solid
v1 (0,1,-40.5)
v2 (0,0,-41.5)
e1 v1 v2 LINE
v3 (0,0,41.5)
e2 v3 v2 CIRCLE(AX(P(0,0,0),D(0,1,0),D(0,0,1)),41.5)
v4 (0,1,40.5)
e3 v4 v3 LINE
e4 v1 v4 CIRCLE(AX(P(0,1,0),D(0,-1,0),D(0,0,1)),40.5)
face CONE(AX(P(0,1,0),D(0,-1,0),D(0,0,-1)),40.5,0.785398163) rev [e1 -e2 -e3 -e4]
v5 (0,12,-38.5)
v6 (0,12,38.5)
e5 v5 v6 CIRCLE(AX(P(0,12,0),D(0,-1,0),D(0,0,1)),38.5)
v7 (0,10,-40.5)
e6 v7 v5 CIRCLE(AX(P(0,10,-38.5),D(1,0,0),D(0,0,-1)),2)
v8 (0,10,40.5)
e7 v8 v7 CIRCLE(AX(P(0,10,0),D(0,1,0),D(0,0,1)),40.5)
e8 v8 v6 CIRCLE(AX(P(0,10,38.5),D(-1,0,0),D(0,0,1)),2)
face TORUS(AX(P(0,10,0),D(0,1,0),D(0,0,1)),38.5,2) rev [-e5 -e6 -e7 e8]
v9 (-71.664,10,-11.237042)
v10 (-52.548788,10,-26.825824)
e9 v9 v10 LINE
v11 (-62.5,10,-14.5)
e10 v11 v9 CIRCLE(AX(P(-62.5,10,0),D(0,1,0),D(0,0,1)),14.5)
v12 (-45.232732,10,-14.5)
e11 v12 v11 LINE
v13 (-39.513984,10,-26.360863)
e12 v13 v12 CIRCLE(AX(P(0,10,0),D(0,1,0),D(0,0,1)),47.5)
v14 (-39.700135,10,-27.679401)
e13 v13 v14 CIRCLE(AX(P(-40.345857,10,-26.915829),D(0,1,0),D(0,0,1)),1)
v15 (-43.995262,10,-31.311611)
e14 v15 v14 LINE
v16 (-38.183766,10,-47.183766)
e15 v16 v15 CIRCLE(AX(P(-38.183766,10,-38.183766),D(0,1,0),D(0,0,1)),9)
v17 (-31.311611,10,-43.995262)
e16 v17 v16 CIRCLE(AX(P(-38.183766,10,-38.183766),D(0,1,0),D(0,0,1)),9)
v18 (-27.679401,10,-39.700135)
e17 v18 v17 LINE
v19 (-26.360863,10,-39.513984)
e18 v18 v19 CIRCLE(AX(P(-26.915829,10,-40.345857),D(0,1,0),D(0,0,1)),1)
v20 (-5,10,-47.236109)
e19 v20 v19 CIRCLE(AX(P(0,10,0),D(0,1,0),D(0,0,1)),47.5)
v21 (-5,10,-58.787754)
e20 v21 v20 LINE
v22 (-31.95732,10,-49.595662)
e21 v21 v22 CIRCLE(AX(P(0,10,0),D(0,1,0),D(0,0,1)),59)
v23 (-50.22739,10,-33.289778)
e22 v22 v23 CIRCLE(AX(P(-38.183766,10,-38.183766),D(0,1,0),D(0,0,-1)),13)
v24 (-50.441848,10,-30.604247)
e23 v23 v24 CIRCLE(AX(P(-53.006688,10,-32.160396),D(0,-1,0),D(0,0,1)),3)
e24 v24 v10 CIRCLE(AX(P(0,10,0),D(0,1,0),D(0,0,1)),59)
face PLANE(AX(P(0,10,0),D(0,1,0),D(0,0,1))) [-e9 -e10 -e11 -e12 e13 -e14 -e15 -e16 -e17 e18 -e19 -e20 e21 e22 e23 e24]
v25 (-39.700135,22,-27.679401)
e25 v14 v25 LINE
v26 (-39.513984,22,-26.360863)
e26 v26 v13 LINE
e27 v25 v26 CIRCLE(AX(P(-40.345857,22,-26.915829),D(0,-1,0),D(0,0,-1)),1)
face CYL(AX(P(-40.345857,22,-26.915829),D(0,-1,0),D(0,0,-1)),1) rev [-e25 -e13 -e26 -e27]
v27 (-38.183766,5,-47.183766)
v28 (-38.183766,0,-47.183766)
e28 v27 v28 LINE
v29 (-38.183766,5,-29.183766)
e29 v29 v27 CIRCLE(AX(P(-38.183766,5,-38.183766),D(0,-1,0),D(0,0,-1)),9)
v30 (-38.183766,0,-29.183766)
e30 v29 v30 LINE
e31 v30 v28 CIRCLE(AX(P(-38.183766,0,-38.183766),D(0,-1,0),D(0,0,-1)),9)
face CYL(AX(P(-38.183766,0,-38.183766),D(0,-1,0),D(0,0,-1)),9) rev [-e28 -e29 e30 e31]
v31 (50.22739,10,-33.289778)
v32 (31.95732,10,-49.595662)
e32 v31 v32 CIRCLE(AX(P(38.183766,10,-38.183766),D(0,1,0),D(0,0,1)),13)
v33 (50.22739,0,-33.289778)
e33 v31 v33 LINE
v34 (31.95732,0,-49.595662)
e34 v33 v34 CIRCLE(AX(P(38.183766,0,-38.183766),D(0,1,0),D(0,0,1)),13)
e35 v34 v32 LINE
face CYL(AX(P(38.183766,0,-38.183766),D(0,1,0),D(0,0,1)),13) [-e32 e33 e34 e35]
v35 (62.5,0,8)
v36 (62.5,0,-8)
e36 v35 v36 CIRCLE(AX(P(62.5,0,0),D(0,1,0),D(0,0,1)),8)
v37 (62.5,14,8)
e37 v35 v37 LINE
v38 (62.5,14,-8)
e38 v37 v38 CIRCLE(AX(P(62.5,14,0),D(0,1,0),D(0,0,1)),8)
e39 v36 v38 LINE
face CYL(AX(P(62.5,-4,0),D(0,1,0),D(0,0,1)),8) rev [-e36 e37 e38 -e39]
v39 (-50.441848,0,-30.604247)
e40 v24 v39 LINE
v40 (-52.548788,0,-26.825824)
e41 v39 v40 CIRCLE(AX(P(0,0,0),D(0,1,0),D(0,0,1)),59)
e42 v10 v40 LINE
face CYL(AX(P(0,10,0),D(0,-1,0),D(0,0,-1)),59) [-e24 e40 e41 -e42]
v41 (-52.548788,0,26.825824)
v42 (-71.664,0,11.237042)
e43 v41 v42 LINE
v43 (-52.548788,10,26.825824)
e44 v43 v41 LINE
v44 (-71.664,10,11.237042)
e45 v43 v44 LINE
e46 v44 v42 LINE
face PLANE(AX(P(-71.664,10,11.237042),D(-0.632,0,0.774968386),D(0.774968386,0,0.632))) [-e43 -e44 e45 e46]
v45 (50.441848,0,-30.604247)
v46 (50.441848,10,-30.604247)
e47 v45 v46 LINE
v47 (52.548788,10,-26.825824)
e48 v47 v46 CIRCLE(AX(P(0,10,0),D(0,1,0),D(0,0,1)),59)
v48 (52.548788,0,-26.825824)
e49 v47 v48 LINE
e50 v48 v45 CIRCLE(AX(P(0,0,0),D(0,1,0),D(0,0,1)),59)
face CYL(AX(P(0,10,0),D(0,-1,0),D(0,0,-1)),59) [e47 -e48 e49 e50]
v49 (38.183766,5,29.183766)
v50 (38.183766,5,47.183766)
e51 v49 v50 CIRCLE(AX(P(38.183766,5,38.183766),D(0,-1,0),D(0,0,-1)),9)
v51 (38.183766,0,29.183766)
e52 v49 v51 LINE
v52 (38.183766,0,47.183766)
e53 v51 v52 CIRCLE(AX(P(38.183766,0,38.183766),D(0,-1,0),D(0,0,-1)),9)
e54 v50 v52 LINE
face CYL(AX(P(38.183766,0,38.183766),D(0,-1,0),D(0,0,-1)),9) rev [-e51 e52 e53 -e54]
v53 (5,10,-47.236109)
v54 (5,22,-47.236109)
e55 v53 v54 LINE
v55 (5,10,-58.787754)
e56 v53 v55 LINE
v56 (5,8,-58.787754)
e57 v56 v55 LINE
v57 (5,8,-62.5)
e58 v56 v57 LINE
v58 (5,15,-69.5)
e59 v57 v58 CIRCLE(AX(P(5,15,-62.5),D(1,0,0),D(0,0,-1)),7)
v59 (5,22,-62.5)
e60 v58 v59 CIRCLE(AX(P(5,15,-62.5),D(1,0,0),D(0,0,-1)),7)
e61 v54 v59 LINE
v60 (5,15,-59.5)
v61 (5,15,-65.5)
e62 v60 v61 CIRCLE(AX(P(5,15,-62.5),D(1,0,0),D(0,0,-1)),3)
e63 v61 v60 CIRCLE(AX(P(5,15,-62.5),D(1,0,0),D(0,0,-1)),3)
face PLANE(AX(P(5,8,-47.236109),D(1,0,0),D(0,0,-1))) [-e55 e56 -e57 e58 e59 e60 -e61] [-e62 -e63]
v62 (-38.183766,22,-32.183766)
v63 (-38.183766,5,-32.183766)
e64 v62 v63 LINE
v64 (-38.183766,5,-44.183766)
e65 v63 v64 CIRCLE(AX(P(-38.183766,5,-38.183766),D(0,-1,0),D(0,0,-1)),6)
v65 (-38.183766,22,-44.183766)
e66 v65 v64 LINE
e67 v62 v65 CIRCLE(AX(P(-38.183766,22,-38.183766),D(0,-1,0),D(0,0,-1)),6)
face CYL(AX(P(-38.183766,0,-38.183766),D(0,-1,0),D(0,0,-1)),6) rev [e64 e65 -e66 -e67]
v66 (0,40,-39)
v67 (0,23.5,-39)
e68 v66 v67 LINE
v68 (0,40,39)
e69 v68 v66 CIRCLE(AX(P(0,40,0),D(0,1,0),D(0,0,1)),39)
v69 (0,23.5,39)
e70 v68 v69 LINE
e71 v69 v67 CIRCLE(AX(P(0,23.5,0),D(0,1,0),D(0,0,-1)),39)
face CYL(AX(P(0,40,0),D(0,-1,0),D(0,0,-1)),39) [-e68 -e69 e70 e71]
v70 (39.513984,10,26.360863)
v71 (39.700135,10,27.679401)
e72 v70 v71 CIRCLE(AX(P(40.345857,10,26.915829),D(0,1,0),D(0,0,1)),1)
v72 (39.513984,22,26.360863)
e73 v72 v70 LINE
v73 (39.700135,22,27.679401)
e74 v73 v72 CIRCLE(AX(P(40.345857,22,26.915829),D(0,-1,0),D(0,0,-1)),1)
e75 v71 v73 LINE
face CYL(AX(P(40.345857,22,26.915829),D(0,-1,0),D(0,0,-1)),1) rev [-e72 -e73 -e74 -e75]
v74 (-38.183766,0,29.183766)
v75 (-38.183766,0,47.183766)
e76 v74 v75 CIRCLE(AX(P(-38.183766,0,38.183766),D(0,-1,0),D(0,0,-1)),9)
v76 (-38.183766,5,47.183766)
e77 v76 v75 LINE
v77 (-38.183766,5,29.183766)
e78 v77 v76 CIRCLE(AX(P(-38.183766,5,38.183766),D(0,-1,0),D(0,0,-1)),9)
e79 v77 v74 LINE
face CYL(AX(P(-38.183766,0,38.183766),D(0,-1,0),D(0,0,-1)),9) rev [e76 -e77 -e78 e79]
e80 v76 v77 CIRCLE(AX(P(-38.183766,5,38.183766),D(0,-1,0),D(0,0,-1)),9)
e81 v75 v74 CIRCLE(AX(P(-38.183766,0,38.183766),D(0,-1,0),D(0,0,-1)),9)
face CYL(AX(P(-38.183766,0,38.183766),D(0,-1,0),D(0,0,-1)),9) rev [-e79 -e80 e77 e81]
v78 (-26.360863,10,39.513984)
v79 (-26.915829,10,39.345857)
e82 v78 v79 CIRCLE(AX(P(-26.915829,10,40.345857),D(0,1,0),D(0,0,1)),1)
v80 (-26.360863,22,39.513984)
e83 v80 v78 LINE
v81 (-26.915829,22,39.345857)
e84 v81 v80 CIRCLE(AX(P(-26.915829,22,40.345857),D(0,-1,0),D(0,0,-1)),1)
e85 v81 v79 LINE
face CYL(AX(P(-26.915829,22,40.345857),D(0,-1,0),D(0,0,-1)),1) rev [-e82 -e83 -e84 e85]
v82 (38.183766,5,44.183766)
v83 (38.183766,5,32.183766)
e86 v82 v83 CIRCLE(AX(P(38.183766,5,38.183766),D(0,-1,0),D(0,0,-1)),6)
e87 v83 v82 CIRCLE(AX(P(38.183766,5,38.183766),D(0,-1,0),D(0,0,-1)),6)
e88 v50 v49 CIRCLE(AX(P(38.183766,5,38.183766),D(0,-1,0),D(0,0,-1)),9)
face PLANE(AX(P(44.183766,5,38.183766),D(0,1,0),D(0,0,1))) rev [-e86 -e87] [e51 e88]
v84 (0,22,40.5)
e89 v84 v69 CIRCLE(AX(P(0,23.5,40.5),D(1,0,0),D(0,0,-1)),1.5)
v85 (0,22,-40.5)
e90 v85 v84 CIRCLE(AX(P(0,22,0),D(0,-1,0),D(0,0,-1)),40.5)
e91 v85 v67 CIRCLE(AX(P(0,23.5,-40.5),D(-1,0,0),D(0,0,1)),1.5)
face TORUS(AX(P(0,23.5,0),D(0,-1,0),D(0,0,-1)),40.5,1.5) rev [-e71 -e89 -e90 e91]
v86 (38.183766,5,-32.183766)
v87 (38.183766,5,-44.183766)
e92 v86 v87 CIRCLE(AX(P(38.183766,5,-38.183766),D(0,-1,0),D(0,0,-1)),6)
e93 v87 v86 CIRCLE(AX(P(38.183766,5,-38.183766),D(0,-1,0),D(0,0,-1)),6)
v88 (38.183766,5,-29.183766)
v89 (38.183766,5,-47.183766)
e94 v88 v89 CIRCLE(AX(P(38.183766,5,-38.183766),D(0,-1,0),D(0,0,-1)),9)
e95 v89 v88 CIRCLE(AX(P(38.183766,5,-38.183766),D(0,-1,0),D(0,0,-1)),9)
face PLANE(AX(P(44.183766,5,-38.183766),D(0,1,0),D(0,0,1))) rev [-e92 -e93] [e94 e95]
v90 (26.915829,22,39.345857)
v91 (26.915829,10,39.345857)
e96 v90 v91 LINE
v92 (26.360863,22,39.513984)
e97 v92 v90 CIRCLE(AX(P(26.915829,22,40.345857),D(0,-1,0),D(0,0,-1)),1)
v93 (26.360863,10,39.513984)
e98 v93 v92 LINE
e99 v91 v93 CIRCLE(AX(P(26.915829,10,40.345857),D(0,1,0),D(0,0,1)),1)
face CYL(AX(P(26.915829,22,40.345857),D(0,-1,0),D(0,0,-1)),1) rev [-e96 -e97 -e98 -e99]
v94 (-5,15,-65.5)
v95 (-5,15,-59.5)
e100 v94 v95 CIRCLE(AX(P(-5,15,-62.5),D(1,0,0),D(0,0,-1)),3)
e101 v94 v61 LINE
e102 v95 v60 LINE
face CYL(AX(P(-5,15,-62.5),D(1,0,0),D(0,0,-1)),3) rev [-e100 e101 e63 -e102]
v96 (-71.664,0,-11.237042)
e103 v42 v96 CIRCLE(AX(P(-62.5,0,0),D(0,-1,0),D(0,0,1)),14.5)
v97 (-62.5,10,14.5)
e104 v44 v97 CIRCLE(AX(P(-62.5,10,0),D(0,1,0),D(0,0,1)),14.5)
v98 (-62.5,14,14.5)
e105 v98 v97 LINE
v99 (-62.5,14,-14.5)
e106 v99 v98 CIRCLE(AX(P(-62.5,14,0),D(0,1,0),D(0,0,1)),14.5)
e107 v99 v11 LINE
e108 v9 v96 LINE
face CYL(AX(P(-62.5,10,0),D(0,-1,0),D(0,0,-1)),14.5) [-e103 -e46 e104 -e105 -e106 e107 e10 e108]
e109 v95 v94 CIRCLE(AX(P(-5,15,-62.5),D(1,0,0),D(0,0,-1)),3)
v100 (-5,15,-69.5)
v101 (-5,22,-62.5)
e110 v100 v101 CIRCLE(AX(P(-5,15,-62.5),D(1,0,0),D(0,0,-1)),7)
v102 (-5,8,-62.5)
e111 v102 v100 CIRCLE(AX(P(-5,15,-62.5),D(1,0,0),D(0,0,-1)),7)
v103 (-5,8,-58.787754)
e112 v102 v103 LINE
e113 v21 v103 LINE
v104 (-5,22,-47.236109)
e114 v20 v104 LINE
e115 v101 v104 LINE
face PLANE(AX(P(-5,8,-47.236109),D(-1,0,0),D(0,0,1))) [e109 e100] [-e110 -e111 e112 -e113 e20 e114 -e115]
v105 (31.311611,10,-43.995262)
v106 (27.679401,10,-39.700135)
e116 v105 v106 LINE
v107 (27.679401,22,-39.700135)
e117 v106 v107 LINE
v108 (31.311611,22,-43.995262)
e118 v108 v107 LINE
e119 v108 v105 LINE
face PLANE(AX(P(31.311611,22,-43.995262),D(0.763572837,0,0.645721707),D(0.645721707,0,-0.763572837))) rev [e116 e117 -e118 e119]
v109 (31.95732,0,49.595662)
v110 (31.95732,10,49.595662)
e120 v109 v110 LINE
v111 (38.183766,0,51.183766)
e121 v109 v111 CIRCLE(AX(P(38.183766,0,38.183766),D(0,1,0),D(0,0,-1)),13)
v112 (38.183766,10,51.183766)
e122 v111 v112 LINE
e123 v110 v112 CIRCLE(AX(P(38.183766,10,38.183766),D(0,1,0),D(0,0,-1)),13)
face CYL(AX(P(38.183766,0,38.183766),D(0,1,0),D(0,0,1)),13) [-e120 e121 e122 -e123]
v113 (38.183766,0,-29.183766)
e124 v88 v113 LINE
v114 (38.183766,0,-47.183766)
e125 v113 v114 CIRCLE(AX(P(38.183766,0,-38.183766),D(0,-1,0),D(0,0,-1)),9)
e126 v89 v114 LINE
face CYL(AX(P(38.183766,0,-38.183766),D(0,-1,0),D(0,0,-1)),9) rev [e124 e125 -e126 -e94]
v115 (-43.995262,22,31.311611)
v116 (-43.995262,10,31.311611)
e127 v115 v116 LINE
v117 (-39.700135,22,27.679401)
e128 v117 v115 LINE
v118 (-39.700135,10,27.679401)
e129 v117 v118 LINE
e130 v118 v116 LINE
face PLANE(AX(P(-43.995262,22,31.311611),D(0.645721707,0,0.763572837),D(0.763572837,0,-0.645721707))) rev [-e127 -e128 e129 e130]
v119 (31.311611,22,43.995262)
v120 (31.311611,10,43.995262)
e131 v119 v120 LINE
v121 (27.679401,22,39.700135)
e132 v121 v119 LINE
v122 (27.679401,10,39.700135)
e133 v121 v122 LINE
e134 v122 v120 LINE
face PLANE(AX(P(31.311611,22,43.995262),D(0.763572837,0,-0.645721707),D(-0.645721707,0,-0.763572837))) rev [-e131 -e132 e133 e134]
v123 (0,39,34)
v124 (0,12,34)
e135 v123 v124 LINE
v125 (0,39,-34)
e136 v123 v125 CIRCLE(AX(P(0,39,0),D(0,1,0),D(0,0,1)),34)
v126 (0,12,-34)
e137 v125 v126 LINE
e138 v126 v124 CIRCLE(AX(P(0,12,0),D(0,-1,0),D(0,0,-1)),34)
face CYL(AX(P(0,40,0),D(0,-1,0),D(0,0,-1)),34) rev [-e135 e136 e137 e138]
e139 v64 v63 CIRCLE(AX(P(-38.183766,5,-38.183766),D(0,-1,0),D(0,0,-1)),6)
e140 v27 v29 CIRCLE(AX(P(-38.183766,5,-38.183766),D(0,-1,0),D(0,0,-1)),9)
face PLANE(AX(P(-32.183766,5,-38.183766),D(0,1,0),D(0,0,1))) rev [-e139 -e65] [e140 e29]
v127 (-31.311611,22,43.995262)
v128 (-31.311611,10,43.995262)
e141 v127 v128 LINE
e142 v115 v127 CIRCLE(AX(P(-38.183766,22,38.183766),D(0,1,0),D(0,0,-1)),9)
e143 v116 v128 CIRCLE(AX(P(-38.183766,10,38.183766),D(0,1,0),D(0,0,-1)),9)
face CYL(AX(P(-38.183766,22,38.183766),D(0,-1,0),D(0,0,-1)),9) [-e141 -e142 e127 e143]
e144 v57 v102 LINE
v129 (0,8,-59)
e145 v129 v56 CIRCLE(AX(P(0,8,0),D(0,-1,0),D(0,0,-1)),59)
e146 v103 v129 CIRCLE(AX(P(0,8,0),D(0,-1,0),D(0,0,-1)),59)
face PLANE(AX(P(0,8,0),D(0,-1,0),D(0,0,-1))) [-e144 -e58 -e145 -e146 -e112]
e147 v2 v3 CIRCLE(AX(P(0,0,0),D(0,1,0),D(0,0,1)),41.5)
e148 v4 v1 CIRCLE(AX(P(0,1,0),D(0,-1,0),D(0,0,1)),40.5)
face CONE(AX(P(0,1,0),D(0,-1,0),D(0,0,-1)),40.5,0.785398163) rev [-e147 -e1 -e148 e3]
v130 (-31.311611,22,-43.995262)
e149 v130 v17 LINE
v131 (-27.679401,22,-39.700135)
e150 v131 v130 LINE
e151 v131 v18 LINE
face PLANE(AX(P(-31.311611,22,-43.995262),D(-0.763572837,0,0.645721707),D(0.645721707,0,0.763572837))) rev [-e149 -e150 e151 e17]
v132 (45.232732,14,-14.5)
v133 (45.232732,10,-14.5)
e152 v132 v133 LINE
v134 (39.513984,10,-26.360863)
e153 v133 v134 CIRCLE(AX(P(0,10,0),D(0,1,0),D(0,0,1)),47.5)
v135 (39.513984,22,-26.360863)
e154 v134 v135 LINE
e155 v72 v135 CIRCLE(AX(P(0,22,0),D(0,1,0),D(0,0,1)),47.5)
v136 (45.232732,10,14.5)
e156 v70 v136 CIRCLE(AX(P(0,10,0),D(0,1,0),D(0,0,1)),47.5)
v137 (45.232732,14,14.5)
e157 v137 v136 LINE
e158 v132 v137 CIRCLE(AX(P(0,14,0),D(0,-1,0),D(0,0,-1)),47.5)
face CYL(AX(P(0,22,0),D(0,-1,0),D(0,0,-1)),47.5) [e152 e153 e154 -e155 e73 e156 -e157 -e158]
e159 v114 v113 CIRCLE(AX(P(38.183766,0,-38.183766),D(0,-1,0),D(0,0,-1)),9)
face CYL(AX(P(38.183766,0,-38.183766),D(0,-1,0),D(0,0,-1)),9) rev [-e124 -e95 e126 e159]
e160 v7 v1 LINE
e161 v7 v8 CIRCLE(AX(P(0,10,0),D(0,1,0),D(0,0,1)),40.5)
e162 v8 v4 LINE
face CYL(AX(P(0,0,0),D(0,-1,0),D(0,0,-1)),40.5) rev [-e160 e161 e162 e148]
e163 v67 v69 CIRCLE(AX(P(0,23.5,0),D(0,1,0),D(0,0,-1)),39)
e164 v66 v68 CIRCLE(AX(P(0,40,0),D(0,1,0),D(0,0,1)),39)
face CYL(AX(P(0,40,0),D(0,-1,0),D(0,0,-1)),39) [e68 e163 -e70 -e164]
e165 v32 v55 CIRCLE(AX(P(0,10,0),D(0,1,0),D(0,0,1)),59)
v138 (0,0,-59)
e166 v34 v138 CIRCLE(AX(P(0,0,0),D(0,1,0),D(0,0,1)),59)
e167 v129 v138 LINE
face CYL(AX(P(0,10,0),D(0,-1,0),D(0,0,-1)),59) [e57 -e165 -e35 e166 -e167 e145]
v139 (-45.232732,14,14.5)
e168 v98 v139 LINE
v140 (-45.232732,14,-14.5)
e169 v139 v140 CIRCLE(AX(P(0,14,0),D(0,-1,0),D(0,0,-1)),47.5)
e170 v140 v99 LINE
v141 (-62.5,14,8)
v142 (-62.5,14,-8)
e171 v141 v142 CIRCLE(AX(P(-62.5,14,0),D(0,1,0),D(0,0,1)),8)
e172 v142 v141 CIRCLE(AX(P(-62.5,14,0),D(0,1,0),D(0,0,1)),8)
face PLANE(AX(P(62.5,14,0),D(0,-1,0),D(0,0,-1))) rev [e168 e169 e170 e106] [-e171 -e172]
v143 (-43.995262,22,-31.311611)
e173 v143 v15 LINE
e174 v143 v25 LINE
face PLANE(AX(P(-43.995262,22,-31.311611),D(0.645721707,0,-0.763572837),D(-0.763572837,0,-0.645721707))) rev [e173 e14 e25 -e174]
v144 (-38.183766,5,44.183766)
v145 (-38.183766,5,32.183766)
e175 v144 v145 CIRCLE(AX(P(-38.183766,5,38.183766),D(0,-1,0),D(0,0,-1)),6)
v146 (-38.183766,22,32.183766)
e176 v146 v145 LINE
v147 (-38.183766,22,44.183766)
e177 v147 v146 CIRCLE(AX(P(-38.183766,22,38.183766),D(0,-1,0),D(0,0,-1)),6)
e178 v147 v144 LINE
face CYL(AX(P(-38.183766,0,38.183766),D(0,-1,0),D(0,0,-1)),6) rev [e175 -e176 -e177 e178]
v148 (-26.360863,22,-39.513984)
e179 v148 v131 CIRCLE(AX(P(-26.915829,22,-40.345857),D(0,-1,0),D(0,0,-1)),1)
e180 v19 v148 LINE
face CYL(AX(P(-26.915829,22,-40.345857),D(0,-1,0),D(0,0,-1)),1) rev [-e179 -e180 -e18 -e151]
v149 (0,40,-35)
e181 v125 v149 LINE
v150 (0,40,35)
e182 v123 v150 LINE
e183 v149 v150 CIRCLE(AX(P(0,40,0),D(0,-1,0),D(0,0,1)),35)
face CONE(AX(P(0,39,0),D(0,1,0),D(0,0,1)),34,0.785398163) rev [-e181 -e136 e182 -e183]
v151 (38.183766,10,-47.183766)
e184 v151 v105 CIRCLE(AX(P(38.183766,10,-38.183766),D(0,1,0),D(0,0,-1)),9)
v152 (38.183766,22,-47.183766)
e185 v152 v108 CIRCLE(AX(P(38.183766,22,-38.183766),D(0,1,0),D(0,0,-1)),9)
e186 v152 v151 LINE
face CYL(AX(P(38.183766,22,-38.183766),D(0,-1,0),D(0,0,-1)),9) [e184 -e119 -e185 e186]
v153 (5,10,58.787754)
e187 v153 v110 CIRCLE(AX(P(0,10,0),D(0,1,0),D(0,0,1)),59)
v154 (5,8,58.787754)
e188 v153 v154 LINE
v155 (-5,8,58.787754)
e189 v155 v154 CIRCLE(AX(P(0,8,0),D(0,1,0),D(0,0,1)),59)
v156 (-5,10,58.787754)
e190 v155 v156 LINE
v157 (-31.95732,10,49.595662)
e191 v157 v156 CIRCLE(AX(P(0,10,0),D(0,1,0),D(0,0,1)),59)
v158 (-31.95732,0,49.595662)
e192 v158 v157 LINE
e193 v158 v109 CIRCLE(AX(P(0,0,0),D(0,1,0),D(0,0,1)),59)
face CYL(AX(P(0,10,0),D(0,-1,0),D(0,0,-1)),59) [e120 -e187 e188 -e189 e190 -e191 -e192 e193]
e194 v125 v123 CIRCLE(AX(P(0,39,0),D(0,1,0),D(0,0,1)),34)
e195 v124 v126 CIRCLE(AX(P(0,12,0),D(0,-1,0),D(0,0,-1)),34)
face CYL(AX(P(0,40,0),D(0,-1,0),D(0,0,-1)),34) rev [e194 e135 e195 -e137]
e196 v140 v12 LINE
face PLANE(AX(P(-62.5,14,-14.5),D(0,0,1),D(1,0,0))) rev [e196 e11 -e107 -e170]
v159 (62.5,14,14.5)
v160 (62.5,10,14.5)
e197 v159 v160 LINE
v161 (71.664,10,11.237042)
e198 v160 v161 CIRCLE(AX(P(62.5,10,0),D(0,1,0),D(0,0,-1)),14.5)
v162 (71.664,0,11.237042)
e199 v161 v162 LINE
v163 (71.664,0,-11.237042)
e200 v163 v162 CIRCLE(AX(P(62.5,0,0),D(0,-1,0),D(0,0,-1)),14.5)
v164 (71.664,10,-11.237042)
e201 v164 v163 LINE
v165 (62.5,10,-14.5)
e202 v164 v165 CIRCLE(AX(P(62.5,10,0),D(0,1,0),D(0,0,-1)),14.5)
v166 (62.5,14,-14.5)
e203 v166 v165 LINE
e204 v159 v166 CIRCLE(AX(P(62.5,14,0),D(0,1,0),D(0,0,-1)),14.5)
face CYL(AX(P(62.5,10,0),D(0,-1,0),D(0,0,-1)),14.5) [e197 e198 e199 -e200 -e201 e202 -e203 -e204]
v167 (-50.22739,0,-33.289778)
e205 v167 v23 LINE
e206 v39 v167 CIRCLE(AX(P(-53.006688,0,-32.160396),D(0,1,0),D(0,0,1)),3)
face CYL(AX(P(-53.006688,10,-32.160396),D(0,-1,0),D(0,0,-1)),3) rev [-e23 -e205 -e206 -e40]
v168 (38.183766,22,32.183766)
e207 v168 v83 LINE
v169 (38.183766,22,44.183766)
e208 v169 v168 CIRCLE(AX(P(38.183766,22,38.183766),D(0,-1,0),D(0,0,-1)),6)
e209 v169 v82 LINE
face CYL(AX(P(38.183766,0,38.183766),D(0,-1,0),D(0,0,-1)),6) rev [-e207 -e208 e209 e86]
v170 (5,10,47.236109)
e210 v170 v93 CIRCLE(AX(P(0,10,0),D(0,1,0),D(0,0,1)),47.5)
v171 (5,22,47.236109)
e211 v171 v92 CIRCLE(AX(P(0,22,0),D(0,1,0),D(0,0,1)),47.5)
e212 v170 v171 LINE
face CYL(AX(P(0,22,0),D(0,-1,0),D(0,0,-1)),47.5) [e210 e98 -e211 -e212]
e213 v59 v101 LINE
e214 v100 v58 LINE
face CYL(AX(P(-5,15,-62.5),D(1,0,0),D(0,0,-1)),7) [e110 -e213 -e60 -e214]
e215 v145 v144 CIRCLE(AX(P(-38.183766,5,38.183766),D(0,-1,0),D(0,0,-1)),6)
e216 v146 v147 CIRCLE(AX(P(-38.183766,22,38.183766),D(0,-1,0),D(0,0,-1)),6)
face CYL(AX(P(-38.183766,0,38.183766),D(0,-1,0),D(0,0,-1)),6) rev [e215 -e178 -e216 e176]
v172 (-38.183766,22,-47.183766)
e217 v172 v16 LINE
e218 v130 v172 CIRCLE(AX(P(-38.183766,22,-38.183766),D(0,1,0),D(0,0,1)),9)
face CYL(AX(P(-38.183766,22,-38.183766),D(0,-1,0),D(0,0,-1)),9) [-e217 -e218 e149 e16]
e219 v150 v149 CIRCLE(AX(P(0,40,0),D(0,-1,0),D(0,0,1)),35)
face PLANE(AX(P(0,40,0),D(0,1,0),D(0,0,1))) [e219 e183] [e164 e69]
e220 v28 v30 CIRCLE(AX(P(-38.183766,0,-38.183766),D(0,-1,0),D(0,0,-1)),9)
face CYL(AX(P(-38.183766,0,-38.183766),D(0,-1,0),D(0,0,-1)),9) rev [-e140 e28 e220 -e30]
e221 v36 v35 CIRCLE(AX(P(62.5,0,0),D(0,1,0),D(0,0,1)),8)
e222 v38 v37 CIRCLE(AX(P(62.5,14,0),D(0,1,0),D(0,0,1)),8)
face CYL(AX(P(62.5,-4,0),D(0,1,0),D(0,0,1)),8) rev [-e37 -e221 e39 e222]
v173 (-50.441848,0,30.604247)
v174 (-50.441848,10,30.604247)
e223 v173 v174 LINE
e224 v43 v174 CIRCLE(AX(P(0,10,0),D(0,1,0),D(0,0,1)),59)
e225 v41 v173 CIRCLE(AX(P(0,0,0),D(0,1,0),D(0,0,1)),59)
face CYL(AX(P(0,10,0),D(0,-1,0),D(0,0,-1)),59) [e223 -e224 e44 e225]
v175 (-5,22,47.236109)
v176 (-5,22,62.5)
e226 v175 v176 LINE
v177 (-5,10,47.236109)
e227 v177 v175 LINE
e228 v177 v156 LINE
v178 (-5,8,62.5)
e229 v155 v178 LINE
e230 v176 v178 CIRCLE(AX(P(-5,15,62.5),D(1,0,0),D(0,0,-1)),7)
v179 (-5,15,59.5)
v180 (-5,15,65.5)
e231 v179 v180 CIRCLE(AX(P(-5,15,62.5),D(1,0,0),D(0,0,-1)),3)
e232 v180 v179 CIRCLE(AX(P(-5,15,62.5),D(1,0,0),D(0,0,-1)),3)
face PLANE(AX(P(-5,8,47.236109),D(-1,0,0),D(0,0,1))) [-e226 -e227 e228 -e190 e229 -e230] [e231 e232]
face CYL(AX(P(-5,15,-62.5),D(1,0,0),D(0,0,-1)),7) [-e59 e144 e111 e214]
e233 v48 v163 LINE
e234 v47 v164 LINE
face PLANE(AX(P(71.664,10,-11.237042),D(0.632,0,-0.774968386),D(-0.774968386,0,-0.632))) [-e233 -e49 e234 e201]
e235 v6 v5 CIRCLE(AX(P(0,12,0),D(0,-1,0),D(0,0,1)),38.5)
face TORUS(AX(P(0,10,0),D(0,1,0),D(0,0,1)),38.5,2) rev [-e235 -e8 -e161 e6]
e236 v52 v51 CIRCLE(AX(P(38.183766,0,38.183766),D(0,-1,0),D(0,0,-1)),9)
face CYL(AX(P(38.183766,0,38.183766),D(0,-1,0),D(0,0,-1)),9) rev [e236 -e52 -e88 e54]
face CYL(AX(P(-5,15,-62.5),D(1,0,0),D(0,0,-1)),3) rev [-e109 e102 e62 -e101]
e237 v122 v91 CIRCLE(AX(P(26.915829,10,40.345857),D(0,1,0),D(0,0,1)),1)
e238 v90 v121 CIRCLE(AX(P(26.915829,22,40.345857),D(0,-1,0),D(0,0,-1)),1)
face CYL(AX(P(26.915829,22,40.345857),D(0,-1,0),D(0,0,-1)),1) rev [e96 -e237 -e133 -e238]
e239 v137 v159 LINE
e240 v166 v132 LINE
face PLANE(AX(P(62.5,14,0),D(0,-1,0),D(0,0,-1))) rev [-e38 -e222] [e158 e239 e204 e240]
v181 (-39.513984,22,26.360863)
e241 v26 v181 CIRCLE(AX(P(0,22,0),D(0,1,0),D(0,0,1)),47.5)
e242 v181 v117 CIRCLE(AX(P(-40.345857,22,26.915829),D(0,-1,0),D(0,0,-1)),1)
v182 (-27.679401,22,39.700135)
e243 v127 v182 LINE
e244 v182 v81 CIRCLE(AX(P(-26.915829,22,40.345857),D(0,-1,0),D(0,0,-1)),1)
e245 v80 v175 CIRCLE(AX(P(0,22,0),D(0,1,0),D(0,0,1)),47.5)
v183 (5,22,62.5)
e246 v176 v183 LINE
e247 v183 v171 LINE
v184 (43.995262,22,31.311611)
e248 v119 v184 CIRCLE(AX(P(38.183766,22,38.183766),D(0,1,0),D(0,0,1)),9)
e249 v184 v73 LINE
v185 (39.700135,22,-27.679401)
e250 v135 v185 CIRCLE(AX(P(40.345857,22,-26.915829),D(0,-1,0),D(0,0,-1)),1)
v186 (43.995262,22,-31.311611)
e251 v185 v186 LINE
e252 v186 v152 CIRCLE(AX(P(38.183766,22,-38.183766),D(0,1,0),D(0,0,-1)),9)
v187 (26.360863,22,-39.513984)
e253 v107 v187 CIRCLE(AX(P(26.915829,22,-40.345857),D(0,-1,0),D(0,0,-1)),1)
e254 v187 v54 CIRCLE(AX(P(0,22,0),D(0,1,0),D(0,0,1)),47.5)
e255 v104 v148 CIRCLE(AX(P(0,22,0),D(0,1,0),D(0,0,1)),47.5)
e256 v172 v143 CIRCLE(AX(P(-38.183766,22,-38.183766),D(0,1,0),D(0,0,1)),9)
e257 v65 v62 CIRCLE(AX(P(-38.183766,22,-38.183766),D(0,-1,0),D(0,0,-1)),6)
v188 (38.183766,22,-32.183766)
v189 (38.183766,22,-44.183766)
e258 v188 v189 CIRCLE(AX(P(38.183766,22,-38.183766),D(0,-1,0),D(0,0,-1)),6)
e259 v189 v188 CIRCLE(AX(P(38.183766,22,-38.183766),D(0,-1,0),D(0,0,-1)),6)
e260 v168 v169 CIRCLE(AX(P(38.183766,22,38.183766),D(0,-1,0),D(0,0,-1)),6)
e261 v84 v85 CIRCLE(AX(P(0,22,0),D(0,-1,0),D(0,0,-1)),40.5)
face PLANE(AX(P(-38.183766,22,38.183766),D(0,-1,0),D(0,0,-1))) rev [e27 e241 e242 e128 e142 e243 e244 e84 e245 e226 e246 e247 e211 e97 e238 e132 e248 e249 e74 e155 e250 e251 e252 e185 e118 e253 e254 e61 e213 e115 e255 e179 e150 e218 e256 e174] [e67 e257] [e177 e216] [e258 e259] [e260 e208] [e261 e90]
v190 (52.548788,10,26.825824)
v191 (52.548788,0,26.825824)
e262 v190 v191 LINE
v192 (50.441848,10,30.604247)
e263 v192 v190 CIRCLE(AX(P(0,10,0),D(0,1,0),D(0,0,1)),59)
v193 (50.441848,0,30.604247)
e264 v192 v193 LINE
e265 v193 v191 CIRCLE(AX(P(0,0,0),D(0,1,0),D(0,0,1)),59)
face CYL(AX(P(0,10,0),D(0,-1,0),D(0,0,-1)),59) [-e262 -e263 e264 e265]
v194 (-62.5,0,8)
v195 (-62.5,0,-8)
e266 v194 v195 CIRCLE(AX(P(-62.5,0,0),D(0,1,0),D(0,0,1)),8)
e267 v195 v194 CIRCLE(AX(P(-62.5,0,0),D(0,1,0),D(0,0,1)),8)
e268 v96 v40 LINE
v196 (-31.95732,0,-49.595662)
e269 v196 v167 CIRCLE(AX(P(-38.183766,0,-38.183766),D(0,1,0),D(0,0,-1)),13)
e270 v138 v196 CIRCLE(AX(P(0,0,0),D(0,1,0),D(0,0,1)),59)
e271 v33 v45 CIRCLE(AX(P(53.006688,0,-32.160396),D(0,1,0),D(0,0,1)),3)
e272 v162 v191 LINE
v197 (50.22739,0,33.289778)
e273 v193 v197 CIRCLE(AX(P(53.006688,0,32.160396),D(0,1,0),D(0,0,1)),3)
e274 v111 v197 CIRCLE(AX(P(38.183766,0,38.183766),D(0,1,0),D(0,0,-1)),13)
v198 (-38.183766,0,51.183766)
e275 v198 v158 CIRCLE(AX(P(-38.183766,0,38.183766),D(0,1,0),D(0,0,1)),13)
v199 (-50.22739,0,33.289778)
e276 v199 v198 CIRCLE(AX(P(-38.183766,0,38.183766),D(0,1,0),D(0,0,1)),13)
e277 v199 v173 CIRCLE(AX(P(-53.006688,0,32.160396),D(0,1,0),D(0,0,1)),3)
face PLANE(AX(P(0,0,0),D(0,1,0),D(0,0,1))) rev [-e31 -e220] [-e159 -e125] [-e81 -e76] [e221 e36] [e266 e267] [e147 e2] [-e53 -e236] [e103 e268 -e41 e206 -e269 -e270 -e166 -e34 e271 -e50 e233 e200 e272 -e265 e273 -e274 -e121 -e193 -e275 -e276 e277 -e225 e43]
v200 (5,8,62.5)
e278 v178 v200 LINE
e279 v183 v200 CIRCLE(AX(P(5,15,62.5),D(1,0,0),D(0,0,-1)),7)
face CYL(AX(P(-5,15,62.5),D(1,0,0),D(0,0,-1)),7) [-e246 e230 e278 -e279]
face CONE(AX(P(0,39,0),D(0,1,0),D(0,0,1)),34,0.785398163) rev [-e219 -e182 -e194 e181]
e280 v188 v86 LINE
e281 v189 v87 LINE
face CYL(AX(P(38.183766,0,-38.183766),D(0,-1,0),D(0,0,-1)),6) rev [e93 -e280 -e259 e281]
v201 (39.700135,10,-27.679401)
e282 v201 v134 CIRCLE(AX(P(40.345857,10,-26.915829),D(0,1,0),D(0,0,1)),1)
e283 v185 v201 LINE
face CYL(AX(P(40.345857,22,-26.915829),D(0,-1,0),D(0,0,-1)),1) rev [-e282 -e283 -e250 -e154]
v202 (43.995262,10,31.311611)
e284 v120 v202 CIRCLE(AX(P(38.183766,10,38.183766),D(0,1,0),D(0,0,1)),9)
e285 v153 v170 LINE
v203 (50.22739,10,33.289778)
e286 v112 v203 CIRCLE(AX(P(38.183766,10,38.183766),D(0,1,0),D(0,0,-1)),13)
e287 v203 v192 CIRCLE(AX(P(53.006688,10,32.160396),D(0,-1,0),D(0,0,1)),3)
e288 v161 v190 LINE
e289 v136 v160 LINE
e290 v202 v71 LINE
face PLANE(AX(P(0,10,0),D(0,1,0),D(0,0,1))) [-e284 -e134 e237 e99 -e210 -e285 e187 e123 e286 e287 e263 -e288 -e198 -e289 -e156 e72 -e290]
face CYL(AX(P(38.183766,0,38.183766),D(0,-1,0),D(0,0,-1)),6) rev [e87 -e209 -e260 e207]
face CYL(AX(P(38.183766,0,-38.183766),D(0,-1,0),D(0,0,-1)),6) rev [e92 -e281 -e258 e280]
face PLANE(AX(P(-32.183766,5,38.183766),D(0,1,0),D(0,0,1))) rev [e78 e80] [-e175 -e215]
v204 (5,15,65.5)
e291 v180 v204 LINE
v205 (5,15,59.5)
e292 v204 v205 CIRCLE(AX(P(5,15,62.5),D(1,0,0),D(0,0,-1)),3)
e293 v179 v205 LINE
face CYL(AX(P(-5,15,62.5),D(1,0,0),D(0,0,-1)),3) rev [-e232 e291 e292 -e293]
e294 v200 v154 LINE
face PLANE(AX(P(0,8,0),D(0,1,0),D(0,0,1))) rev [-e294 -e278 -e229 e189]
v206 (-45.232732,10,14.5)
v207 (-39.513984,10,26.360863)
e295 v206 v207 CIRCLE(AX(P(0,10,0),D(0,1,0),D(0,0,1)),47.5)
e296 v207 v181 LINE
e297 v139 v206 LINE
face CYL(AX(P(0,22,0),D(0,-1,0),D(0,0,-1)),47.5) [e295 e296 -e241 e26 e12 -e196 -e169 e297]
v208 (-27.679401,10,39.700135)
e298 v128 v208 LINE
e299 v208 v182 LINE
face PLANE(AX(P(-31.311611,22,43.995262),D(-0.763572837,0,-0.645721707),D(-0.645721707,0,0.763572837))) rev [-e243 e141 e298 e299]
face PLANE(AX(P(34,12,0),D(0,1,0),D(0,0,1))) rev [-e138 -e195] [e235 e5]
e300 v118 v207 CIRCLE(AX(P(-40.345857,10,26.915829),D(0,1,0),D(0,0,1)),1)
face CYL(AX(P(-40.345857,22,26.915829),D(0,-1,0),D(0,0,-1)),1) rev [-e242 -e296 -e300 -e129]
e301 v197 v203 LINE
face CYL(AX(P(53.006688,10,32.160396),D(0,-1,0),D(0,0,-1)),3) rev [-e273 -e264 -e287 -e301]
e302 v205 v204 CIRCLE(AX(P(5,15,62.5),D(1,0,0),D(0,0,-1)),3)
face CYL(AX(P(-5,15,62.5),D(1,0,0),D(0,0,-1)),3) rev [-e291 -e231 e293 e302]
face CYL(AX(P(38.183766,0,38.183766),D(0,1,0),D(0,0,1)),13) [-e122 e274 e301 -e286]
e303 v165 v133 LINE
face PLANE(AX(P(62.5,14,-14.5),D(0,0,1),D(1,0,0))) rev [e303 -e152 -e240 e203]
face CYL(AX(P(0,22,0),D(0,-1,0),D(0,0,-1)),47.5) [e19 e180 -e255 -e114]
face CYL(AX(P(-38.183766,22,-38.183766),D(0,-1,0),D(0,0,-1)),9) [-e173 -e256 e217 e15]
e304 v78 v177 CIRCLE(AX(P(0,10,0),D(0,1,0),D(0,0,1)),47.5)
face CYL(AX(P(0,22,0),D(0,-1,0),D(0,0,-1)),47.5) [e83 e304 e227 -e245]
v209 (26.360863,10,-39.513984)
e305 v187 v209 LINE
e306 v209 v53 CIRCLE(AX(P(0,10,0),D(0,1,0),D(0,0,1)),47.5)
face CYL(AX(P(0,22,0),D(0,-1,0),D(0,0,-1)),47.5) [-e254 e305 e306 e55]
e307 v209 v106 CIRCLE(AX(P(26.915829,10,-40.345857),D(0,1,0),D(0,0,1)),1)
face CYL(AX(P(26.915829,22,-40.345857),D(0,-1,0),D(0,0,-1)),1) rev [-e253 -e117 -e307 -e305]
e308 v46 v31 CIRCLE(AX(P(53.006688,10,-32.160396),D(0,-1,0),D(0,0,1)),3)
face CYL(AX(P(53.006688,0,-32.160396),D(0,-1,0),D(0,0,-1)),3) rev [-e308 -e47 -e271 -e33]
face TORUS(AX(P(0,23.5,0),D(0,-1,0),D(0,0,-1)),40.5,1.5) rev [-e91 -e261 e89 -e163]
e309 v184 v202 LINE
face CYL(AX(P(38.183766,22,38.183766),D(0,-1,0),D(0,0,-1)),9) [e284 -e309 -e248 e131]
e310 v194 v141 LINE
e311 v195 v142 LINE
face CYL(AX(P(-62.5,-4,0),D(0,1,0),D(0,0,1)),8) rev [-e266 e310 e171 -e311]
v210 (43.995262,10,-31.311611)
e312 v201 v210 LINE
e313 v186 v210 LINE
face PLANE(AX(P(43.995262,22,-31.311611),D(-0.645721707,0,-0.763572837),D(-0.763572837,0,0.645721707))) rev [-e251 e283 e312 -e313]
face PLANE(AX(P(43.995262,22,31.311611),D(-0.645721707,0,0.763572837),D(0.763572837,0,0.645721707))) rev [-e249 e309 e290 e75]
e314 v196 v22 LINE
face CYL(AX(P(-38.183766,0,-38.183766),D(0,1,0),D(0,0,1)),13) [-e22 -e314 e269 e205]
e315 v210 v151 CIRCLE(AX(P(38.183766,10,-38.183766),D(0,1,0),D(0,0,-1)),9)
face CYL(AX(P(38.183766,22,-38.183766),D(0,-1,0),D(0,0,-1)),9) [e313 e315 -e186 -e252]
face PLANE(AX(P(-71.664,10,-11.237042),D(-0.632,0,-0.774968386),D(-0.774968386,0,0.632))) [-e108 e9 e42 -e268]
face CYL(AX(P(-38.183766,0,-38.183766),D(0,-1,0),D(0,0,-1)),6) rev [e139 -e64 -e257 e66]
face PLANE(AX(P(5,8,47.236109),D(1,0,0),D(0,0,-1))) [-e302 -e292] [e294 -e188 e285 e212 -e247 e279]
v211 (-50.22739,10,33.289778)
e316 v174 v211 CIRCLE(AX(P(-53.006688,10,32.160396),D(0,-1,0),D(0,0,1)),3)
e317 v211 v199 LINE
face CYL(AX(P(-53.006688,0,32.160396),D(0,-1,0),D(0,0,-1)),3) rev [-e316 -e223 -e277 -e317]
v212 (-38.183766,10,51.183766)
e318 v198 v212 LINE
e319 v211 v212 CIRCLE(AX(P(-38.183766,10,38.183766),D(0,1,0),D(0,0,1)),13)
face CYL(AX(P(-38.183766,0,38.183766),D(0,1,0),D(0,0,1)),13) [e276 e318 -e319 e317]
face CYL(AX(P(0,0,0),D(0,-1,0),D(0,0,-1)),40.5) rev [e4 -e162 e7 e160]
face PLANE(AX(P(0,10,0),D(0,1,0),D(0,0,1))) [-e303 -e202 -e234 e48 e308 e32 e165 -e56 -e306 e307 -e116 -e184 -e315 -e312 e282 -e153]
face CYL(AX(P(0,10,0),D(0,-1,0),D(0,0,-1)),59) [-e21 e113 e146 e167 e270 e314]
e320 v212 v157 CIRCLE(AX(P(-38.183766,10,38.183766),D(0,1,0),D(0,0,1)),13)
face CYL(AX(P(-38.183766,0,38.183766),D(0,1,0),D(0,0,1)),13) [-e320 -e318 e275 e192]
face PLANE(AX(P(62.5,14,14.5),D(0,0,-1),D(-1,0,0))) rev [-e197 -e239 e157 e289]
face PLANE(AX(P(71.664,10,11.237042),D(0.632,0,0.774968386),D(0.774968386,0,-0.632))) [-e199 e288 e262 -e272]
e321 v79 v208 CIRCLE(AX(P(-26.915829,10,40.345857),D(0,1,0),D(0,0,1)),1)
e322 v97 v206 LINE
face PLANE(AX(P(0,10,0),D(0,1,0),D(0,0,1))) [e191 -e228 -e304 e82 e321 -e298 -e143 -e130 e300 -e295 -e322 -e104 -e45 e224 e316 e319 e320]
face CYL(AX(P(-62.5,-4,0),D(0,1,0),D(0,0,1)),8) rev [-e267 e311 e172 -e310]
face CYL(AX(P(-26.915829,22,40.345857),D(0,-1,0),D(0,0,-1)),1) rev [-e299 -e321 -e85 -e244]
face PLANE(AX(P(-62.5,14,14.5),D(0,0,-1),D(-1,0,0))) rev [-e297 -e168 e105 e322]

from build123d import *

# Parameters (mm, degrees)
BASE_DISC_SKETCH_R                 = 59
BASE_DISC_118_DEPTH                = 10
LUG_FLANGE_DEPTH                   = 10
LUG_START                          = -10
LUG_PADS_DEPTH                     = 10
HUB_BOSS_DEPTH                     = 12
SIDE_TAB_WEB_DEPTH                 = 4
COLLAR_RING_SKETCH_R               = 39
COLLAR_RING_SKETCH_R_2             = 34
COLLAR_RING_78_DEPTH               = 18
COLLAR_ROOT_FILLET_R1_5_R          = 1.5
COLLAR_TOP_CHAMFER_1X45_SIZE       = 1
TAB_SLOT_SKETCH_R                  = 8
TAB_SLOT_16_DEPTH                  = 18
LUG_HOLES_12_C_BORE_18_D           = 12
LUG_HOLES_12_C_BORE_18_DEPTH       = 99.95498987
LUG_HOLES_12_C_BORE_18_CBORE_D     = 18
LUG_HOLES_12_C_BORE_18_CBORE_DEPTH = 5
BORE_68_C_BORE_81_D                = 68
BORE_68_C_BORE_81_DEPTH            = 99.788526395
BORE_68_C_BORE_81_CBORE_D          = 81
BORE_68_C_BORE_81_CBORE_DEPTH      = 12
BORE_FILLET_R2_R                   = 2
BORE_CHAMFER_1X45_SIZE             = 1
MOUNTING_EARS_DEPTH                = 12
MOUNTING_EARS_DEPTH_BACK           = 2
MOUNTING_EAR_SKETCH_W              = 10
MOUNTING_EAR_SKETCH_H              = 15.263890931
EAR_BOSS_SKETCH_R                  = 7
EAR_BOSSES_DEPTH                   = 10
EAR_HOLE_SKETCH_R                  = 3
EAR_HOLES_6_DEPTH                  = 10
LUG_PAD_FILLET_R3_R                = 3
HUB_BOSS_EDGE_FILLET_R1_R          = 1


with BuildPart() as part:
    # Base Disc Sketch → Base Disc Ø118 (new body)
    with BuildSketch(Plane(origin=(0, 0, 0), x_dir=(1, 0, 0), z_dir=(0, 1, 0))):
        with Locations(Location((0, 0, 0), (0, 0, 270))):
            Circle(BASE_DISC_SKETCH_R)
    extrude(amount=BASE_DISC_118_DEPTH)

    # Lug Flange Sketch → Lug Flange (add)
    with BuildSketch(Plane.XZ):
        with BuildLine():
            Line((71.664, 11.237041604), (52.548788257, 26.825824363))
            ThreePointArc((52.548788257, 26.825824363), (0, 59), (-52.548788257, 26.825824363))
            Line((-52.548788257, 26.825824363), (-71.664, 11.237041604))
            ThreePointArc((-71.664, 11.237041604), (-77, 0), (-71.664, -11.237041604))
            Line((-71.664, -11.237041604), (-52.548788257, -26.825824363))
            ThreePointArc((-52.548788257, -26.825824363), (0, -59), (52.548788257, -26.825824363))
            Line((52.548788257, -26.825824363), (71.664, -11.237041604))
            ThreePointArc((71.664, -11.237041604), (77, 0), (71.664, 11.237041604))
        make_face()
    extrude(amount=-LUG_FLANGE_DEPTH)

    # Lug Pads Sketch → Lug Pads (add)
    with BuildSketch(Plane(origin=(0, 10, 0), x_dir=(1, 0, 0), z_dir=(0, 1, 0)).offset(LUG_START)):
        with BuildLine():
            ThreePointArc((-49.595662085, -31.957320012), (-47.376154339, -47.376154339), (-31.957320012, -49.595662085))
            ThreePointArc((-31.957320012, -49.595662085), (0, -59), (31.957320012, -49.595662085))
            ThreePointArc((31.957320012, -49.595662085), (47.376154339, -47.376154339), (49.595662085, -31.957320012))
            ThreePointArc((49.595662085, -31.957320012), (59, 0), (49.595662085, 31.957320012))
            ThreePointArc((49.595662085, 31.957320012), (47.376154339, 47.376154339), (31.957320012, 49.595662085))
            ThreePointArc((31.957320012, 49.595662085), (0, 59), (-31.957320012, 49.595662085))
            ThreePointArc((-31.957320012, 49.595662085), (-47.376154339, 47.376154339), (-49.595662085, 31.957320012))
            ThreePointArc((-49.595662085, 31.957320012), (-59, 0), (-49.595662085, -31.957320012))
        make_face()
    extrude(amount=LUG_PADS_DEPTH)

    # Hub Boss Sketch → Hub Boss (add)
    with BuildSketch(Plane(origin=(0, 10, 0), x_dir=(1, 0, 0), z_dir=(0, 1, 0))):
        with BuildLine():
            Line((-31.311610651, -43.995261545), (-27.097752399, -39.012329012))
            ThreePointArc((-27.097752399, -39.012329012), (0, -47.5), (27.097752399, -39.012329012))
            Line((27.097752399, -39.012329012), (31.311610651, -43.995261545))
            ThreePointArc((31.311610651, -43.995261545), (44.547727215, -44.547727215), (43.995261545, -31.311610651))
            Line((43.995261545, -31.311610651), (39.012329012, -27.097752399))
            ThreePointArc((39.012329012, -27.097752399), (47.5, 0), (39.012329012, 27.097752399))
            Line((39.012329012, 27.097752399), (43.995261545, 31.311610651))
            ThreePointArc((43.995261545, 31.311610651), (44.547727215, 44.547727215), (31.311610651, 43.995261545))
            Line((31.311610651, 43.995261545), (27.097752399, 39.012329012))
            ThreePointArc((27.097752399, 39.012329012), (0, 47.5), (-27.097752399, 39.012329012))
            Line((-27.097752399, 39.012329012), (-31.311610651, 43.995261545))
            ThreePointArc((-31.311610651, 43.995261545), (-44.547727215, 44.547727215), (-43.995261545, 31.311610651))
            Line((-43.995261545, 31.311610651), (-39.012329012, 27.097752399))
            ThreePointArc((-39.012329012, 27.097752399), (-47.5, 0), (-39.012329012, -27.097752399))
            Line((-39.012329012, -27.097752399), (-43.995261545, -31.311610651))
            ThreePointArc((-43.995261545, -31.311610651), (-44.547727215, -44.547727215), (-31.311610651, -43.995261545))
        make_face()
    extrude(amount=HUB_BOSS_DEPTH)

    # Side Tab Sketch → Side Tab Web (add)
    with BuildSketch(Plane(origin=(0, 10, 0), x_dir=(1, 0, 0), z_dir=(0, 1, 0))):
        with BuildLine():
            Line((-62.5, 14.5), (-45.232731512, 14.5))
            ThreePointArc((-45.232731512, 14.5), (0, 47.5), (45.232731512, 14.5))
            Line((45.232731512, 14.5), (62.5, 14.5))
            ThreePointArc((62.5, 14.5), (77, 0), (62.5, -14.5))
            Line((62.5, -14.5), (45.232731512, -14.5))
            ThreePointArc((45.232731512, -14.5), (0, -47.5), (-45.232731512, -14.5))
            Line((-45.232731512, -14.5), (-62.5, -14.5))
            ThreePointArc((-62.5, -14.5), (-77, 0), (-62.5, 14.5))
        make_face()
    extrude(amount=SIDE_TAB_WEB_DEPTH)

    # Collar Ring Sketch → Collar Ring Ø78 (add)
    with BuildSketch(Plane(origin=(0, 22, 0), x_dir=(1, 0, 0), z_dir=(0, 1, 0))):
        with Locations(Location((0, 0, 0), (0, 0, 90))):
            Circle(COLLAR_RING_SKETCH_R)
        with Locations(Location((0, 0, 0), (0, 0, 270))):
            Circle(COLLAR_RING_SKETCH_R_2, mode=Mode.SUBTRACT)
    extrude(amount=COLLAR_RING_78_DEPTH)

    # Collar Root Fillet R1.5
    collar_root_fillet_r1_5_edges = [part.edges().sort_by_distance(p)[0] for p in [
        (0, 22, 39),
    ]]
    fillet(collar_root_fillet_r1_5_edges, radius=COLLAR_ROOT_FILLET_R1_5_R)

    # Collar Top Chamfer 1x45
    collar_top_chamfer_1x45_edges = [part.edges().sort_by_distance(p)[0] for p in [
        (0, 40, -34),
    ]]
    chamfer(collar_top_chamfer_1x45_edges, length=COLLAR_TOP_CHAMFER_1X45_SIZE)

    # Tab Slot Sketch → Tab Slot 16 (cut)
    with BuildSketch(Plane(origin=(0, 14, 0), x_dir=(1, 0, 0), z_dir=(0, 1, 0))):
        with Locations(Location((-62.5, 0, 0), (0, 0, 270))):
            Circle(TAB_SLOT_SKETCH_R)
        with Locations(Location((62.5, 0, 0), (0, 0, 270))):
            Circle(TAB_SLOT_SKETCH_R)
    extrude(amount=-TAB_SLOT_16_DEPTH, mode=Mode.SUBTRACT)

    # Lug Holes Ø12 C-Bore Ø18
    with Locations(Plane(origin=(-38.183766184, 0, 38.183766184), x_dir=(0, 0, -1), z_dir=(0, -1, 0))):
        with Locations((0, 0), (0, 76.367532368), (76.367532368, 76.367532368), (76.367532368, 0)):
            CounterBoreHole(LUG_HOLES_12_C_BORE_18_D / 2, LUG_HOLES_12_C_BORE_18_CBORE_D / 2, LUG_HOLES_12_C_BORE_18_CBORE_DEPTH, depth=LUG_HOLES_12_C_BORE_18_DEPTH)

    # Bore Ø68 C-Bore Ø81
    with Locations(Plane(origin=(0, 0, 0), x_dir=(0, 0, -1), z_dir=(0, -1, 0))):
        with Locations((0, 0)):
            CounterBoreHole(BORE_68_C_BORE_81_D / 2, BORE_68_C_BORE_81_CBORE_D / 2, BORE_68_C_BORE_81_CBORE_DEPTH, depth=BORE_68_C_BORE_81_DEPTH)

    # Bore Fillet R2
    bore_fillet_r2_edges = [part.edges().sort_by_distance(p)[0] for p in [
        (0, 12, 40.5),
    ]]
    fillet(bore_fillet_r2_edges, radius=BORE_FILLET_R2_R)

    # Bore Chamfer 1x45
    bore_chamfer_1x45_edges = [part.edges().sort_by_distance(p)[0] for p in [
        (0, 0, 40.5),
    ]]
    chamfer(bore_chamfer_1x45_edges, length=BORE_CHAMFER_1X45_SIZE)

    # Mounting Ear Sketch → Mounting Ears (add, two sides: drawn at the far end of the back side and taken through both)
    with BuildSketch(Plane(origin=(0, 10, 0), x_dir=(1, 0, 0), z_dir=(0, 1, 0)).offset(-MOUNTING_EARS_DEPTH_BACK)):
        with Locations((0, 54.868054535)):
            Rectangle(MOUNTING_EAR_SKETCH_W, MOUNTING_EAR_SKETCH_H)
        with Locations((0, -54.868054535)):
            Rectangle(MOUNTING_EAR_SKETCH_W, MOUNTING_EAR_SKETCH_H)
    extrude(amount=MOUNTING_EARS_DEPTH + MOUNTING_EARS_DEPTH_BACK)

    # Ear Boss Sketch → Ear Bosses (add)
    with BuildSketch(Plane(origin=(5, 0, 0), x_dir=(0, 0, -1), z_dir=(1, 0, 0))):
        with Locations((62.5, 15)):
            Circle(EAR_BOSS_SKETCH_R)
        with Locations((-62.5, 15)):
            Circle(EAR_BOSS_SKETCH_R)
    extrude(amount=-EAR_BOSSES_DEPTH)

    # Ear Hole Sketch → Ear Holes Ø6 (cut)
    with BuildSketch(Plane(origin=(5, 0, 0), x_dir=(0, 0, -1), z_dir=(1, 0, 0))):
        with Locations((-62.5, 15)):
            Circle(EAR_HOLE_SKETCH_R)
        with Locations((62.5, 15)):
            Circle(EAR_HOLE_SKETCH_R)
    extrude(amount=-EAR_HOLES_6_DEPTH, mode=Mode.SUBTRACT)

    # Lug Pad Fillet R3
    lug_pad_fillet_r3_edges = [part.edges().sort_by_distance(p)[0] for p in [
        (-49.595662085, 5, 31.957320012),
        (49.595662085, 5, -31.957320012),
        (-49.595662085, 5, -31.957320012),
        (49.595662085, 5, 31.957320012),
    ]]
    fillet(lug_pad_fillet_r3_edges, radius=LUG_PAD_FILLET_R3_R)

    # Hub Boss Edge Fillet R1
    hub_boss_edge_fillet_r1_edges = [part.edges().sort_by_distance(p)[0] for p in [
        (-27.097752399, 16, 39.012329012),
        (27.097752399, 16, 39.012329012),
        (39.012329012, 16, 27.097752399),
        (39.012329012, 16, -27.097752399),
        (27.097752399, 16, -39.012329012),
        (-27.097752399, 16, -39.012329012),
        (-39.012329012, 16, -27.097752399),
        (-39.012329012, 16, 27.097752399),
    ]]
    fillet(hub_boss_edge_fillet_r1_edges, radius=HUB_BOSS_EDGE_FILLET_R1_R)


solid = part.part
